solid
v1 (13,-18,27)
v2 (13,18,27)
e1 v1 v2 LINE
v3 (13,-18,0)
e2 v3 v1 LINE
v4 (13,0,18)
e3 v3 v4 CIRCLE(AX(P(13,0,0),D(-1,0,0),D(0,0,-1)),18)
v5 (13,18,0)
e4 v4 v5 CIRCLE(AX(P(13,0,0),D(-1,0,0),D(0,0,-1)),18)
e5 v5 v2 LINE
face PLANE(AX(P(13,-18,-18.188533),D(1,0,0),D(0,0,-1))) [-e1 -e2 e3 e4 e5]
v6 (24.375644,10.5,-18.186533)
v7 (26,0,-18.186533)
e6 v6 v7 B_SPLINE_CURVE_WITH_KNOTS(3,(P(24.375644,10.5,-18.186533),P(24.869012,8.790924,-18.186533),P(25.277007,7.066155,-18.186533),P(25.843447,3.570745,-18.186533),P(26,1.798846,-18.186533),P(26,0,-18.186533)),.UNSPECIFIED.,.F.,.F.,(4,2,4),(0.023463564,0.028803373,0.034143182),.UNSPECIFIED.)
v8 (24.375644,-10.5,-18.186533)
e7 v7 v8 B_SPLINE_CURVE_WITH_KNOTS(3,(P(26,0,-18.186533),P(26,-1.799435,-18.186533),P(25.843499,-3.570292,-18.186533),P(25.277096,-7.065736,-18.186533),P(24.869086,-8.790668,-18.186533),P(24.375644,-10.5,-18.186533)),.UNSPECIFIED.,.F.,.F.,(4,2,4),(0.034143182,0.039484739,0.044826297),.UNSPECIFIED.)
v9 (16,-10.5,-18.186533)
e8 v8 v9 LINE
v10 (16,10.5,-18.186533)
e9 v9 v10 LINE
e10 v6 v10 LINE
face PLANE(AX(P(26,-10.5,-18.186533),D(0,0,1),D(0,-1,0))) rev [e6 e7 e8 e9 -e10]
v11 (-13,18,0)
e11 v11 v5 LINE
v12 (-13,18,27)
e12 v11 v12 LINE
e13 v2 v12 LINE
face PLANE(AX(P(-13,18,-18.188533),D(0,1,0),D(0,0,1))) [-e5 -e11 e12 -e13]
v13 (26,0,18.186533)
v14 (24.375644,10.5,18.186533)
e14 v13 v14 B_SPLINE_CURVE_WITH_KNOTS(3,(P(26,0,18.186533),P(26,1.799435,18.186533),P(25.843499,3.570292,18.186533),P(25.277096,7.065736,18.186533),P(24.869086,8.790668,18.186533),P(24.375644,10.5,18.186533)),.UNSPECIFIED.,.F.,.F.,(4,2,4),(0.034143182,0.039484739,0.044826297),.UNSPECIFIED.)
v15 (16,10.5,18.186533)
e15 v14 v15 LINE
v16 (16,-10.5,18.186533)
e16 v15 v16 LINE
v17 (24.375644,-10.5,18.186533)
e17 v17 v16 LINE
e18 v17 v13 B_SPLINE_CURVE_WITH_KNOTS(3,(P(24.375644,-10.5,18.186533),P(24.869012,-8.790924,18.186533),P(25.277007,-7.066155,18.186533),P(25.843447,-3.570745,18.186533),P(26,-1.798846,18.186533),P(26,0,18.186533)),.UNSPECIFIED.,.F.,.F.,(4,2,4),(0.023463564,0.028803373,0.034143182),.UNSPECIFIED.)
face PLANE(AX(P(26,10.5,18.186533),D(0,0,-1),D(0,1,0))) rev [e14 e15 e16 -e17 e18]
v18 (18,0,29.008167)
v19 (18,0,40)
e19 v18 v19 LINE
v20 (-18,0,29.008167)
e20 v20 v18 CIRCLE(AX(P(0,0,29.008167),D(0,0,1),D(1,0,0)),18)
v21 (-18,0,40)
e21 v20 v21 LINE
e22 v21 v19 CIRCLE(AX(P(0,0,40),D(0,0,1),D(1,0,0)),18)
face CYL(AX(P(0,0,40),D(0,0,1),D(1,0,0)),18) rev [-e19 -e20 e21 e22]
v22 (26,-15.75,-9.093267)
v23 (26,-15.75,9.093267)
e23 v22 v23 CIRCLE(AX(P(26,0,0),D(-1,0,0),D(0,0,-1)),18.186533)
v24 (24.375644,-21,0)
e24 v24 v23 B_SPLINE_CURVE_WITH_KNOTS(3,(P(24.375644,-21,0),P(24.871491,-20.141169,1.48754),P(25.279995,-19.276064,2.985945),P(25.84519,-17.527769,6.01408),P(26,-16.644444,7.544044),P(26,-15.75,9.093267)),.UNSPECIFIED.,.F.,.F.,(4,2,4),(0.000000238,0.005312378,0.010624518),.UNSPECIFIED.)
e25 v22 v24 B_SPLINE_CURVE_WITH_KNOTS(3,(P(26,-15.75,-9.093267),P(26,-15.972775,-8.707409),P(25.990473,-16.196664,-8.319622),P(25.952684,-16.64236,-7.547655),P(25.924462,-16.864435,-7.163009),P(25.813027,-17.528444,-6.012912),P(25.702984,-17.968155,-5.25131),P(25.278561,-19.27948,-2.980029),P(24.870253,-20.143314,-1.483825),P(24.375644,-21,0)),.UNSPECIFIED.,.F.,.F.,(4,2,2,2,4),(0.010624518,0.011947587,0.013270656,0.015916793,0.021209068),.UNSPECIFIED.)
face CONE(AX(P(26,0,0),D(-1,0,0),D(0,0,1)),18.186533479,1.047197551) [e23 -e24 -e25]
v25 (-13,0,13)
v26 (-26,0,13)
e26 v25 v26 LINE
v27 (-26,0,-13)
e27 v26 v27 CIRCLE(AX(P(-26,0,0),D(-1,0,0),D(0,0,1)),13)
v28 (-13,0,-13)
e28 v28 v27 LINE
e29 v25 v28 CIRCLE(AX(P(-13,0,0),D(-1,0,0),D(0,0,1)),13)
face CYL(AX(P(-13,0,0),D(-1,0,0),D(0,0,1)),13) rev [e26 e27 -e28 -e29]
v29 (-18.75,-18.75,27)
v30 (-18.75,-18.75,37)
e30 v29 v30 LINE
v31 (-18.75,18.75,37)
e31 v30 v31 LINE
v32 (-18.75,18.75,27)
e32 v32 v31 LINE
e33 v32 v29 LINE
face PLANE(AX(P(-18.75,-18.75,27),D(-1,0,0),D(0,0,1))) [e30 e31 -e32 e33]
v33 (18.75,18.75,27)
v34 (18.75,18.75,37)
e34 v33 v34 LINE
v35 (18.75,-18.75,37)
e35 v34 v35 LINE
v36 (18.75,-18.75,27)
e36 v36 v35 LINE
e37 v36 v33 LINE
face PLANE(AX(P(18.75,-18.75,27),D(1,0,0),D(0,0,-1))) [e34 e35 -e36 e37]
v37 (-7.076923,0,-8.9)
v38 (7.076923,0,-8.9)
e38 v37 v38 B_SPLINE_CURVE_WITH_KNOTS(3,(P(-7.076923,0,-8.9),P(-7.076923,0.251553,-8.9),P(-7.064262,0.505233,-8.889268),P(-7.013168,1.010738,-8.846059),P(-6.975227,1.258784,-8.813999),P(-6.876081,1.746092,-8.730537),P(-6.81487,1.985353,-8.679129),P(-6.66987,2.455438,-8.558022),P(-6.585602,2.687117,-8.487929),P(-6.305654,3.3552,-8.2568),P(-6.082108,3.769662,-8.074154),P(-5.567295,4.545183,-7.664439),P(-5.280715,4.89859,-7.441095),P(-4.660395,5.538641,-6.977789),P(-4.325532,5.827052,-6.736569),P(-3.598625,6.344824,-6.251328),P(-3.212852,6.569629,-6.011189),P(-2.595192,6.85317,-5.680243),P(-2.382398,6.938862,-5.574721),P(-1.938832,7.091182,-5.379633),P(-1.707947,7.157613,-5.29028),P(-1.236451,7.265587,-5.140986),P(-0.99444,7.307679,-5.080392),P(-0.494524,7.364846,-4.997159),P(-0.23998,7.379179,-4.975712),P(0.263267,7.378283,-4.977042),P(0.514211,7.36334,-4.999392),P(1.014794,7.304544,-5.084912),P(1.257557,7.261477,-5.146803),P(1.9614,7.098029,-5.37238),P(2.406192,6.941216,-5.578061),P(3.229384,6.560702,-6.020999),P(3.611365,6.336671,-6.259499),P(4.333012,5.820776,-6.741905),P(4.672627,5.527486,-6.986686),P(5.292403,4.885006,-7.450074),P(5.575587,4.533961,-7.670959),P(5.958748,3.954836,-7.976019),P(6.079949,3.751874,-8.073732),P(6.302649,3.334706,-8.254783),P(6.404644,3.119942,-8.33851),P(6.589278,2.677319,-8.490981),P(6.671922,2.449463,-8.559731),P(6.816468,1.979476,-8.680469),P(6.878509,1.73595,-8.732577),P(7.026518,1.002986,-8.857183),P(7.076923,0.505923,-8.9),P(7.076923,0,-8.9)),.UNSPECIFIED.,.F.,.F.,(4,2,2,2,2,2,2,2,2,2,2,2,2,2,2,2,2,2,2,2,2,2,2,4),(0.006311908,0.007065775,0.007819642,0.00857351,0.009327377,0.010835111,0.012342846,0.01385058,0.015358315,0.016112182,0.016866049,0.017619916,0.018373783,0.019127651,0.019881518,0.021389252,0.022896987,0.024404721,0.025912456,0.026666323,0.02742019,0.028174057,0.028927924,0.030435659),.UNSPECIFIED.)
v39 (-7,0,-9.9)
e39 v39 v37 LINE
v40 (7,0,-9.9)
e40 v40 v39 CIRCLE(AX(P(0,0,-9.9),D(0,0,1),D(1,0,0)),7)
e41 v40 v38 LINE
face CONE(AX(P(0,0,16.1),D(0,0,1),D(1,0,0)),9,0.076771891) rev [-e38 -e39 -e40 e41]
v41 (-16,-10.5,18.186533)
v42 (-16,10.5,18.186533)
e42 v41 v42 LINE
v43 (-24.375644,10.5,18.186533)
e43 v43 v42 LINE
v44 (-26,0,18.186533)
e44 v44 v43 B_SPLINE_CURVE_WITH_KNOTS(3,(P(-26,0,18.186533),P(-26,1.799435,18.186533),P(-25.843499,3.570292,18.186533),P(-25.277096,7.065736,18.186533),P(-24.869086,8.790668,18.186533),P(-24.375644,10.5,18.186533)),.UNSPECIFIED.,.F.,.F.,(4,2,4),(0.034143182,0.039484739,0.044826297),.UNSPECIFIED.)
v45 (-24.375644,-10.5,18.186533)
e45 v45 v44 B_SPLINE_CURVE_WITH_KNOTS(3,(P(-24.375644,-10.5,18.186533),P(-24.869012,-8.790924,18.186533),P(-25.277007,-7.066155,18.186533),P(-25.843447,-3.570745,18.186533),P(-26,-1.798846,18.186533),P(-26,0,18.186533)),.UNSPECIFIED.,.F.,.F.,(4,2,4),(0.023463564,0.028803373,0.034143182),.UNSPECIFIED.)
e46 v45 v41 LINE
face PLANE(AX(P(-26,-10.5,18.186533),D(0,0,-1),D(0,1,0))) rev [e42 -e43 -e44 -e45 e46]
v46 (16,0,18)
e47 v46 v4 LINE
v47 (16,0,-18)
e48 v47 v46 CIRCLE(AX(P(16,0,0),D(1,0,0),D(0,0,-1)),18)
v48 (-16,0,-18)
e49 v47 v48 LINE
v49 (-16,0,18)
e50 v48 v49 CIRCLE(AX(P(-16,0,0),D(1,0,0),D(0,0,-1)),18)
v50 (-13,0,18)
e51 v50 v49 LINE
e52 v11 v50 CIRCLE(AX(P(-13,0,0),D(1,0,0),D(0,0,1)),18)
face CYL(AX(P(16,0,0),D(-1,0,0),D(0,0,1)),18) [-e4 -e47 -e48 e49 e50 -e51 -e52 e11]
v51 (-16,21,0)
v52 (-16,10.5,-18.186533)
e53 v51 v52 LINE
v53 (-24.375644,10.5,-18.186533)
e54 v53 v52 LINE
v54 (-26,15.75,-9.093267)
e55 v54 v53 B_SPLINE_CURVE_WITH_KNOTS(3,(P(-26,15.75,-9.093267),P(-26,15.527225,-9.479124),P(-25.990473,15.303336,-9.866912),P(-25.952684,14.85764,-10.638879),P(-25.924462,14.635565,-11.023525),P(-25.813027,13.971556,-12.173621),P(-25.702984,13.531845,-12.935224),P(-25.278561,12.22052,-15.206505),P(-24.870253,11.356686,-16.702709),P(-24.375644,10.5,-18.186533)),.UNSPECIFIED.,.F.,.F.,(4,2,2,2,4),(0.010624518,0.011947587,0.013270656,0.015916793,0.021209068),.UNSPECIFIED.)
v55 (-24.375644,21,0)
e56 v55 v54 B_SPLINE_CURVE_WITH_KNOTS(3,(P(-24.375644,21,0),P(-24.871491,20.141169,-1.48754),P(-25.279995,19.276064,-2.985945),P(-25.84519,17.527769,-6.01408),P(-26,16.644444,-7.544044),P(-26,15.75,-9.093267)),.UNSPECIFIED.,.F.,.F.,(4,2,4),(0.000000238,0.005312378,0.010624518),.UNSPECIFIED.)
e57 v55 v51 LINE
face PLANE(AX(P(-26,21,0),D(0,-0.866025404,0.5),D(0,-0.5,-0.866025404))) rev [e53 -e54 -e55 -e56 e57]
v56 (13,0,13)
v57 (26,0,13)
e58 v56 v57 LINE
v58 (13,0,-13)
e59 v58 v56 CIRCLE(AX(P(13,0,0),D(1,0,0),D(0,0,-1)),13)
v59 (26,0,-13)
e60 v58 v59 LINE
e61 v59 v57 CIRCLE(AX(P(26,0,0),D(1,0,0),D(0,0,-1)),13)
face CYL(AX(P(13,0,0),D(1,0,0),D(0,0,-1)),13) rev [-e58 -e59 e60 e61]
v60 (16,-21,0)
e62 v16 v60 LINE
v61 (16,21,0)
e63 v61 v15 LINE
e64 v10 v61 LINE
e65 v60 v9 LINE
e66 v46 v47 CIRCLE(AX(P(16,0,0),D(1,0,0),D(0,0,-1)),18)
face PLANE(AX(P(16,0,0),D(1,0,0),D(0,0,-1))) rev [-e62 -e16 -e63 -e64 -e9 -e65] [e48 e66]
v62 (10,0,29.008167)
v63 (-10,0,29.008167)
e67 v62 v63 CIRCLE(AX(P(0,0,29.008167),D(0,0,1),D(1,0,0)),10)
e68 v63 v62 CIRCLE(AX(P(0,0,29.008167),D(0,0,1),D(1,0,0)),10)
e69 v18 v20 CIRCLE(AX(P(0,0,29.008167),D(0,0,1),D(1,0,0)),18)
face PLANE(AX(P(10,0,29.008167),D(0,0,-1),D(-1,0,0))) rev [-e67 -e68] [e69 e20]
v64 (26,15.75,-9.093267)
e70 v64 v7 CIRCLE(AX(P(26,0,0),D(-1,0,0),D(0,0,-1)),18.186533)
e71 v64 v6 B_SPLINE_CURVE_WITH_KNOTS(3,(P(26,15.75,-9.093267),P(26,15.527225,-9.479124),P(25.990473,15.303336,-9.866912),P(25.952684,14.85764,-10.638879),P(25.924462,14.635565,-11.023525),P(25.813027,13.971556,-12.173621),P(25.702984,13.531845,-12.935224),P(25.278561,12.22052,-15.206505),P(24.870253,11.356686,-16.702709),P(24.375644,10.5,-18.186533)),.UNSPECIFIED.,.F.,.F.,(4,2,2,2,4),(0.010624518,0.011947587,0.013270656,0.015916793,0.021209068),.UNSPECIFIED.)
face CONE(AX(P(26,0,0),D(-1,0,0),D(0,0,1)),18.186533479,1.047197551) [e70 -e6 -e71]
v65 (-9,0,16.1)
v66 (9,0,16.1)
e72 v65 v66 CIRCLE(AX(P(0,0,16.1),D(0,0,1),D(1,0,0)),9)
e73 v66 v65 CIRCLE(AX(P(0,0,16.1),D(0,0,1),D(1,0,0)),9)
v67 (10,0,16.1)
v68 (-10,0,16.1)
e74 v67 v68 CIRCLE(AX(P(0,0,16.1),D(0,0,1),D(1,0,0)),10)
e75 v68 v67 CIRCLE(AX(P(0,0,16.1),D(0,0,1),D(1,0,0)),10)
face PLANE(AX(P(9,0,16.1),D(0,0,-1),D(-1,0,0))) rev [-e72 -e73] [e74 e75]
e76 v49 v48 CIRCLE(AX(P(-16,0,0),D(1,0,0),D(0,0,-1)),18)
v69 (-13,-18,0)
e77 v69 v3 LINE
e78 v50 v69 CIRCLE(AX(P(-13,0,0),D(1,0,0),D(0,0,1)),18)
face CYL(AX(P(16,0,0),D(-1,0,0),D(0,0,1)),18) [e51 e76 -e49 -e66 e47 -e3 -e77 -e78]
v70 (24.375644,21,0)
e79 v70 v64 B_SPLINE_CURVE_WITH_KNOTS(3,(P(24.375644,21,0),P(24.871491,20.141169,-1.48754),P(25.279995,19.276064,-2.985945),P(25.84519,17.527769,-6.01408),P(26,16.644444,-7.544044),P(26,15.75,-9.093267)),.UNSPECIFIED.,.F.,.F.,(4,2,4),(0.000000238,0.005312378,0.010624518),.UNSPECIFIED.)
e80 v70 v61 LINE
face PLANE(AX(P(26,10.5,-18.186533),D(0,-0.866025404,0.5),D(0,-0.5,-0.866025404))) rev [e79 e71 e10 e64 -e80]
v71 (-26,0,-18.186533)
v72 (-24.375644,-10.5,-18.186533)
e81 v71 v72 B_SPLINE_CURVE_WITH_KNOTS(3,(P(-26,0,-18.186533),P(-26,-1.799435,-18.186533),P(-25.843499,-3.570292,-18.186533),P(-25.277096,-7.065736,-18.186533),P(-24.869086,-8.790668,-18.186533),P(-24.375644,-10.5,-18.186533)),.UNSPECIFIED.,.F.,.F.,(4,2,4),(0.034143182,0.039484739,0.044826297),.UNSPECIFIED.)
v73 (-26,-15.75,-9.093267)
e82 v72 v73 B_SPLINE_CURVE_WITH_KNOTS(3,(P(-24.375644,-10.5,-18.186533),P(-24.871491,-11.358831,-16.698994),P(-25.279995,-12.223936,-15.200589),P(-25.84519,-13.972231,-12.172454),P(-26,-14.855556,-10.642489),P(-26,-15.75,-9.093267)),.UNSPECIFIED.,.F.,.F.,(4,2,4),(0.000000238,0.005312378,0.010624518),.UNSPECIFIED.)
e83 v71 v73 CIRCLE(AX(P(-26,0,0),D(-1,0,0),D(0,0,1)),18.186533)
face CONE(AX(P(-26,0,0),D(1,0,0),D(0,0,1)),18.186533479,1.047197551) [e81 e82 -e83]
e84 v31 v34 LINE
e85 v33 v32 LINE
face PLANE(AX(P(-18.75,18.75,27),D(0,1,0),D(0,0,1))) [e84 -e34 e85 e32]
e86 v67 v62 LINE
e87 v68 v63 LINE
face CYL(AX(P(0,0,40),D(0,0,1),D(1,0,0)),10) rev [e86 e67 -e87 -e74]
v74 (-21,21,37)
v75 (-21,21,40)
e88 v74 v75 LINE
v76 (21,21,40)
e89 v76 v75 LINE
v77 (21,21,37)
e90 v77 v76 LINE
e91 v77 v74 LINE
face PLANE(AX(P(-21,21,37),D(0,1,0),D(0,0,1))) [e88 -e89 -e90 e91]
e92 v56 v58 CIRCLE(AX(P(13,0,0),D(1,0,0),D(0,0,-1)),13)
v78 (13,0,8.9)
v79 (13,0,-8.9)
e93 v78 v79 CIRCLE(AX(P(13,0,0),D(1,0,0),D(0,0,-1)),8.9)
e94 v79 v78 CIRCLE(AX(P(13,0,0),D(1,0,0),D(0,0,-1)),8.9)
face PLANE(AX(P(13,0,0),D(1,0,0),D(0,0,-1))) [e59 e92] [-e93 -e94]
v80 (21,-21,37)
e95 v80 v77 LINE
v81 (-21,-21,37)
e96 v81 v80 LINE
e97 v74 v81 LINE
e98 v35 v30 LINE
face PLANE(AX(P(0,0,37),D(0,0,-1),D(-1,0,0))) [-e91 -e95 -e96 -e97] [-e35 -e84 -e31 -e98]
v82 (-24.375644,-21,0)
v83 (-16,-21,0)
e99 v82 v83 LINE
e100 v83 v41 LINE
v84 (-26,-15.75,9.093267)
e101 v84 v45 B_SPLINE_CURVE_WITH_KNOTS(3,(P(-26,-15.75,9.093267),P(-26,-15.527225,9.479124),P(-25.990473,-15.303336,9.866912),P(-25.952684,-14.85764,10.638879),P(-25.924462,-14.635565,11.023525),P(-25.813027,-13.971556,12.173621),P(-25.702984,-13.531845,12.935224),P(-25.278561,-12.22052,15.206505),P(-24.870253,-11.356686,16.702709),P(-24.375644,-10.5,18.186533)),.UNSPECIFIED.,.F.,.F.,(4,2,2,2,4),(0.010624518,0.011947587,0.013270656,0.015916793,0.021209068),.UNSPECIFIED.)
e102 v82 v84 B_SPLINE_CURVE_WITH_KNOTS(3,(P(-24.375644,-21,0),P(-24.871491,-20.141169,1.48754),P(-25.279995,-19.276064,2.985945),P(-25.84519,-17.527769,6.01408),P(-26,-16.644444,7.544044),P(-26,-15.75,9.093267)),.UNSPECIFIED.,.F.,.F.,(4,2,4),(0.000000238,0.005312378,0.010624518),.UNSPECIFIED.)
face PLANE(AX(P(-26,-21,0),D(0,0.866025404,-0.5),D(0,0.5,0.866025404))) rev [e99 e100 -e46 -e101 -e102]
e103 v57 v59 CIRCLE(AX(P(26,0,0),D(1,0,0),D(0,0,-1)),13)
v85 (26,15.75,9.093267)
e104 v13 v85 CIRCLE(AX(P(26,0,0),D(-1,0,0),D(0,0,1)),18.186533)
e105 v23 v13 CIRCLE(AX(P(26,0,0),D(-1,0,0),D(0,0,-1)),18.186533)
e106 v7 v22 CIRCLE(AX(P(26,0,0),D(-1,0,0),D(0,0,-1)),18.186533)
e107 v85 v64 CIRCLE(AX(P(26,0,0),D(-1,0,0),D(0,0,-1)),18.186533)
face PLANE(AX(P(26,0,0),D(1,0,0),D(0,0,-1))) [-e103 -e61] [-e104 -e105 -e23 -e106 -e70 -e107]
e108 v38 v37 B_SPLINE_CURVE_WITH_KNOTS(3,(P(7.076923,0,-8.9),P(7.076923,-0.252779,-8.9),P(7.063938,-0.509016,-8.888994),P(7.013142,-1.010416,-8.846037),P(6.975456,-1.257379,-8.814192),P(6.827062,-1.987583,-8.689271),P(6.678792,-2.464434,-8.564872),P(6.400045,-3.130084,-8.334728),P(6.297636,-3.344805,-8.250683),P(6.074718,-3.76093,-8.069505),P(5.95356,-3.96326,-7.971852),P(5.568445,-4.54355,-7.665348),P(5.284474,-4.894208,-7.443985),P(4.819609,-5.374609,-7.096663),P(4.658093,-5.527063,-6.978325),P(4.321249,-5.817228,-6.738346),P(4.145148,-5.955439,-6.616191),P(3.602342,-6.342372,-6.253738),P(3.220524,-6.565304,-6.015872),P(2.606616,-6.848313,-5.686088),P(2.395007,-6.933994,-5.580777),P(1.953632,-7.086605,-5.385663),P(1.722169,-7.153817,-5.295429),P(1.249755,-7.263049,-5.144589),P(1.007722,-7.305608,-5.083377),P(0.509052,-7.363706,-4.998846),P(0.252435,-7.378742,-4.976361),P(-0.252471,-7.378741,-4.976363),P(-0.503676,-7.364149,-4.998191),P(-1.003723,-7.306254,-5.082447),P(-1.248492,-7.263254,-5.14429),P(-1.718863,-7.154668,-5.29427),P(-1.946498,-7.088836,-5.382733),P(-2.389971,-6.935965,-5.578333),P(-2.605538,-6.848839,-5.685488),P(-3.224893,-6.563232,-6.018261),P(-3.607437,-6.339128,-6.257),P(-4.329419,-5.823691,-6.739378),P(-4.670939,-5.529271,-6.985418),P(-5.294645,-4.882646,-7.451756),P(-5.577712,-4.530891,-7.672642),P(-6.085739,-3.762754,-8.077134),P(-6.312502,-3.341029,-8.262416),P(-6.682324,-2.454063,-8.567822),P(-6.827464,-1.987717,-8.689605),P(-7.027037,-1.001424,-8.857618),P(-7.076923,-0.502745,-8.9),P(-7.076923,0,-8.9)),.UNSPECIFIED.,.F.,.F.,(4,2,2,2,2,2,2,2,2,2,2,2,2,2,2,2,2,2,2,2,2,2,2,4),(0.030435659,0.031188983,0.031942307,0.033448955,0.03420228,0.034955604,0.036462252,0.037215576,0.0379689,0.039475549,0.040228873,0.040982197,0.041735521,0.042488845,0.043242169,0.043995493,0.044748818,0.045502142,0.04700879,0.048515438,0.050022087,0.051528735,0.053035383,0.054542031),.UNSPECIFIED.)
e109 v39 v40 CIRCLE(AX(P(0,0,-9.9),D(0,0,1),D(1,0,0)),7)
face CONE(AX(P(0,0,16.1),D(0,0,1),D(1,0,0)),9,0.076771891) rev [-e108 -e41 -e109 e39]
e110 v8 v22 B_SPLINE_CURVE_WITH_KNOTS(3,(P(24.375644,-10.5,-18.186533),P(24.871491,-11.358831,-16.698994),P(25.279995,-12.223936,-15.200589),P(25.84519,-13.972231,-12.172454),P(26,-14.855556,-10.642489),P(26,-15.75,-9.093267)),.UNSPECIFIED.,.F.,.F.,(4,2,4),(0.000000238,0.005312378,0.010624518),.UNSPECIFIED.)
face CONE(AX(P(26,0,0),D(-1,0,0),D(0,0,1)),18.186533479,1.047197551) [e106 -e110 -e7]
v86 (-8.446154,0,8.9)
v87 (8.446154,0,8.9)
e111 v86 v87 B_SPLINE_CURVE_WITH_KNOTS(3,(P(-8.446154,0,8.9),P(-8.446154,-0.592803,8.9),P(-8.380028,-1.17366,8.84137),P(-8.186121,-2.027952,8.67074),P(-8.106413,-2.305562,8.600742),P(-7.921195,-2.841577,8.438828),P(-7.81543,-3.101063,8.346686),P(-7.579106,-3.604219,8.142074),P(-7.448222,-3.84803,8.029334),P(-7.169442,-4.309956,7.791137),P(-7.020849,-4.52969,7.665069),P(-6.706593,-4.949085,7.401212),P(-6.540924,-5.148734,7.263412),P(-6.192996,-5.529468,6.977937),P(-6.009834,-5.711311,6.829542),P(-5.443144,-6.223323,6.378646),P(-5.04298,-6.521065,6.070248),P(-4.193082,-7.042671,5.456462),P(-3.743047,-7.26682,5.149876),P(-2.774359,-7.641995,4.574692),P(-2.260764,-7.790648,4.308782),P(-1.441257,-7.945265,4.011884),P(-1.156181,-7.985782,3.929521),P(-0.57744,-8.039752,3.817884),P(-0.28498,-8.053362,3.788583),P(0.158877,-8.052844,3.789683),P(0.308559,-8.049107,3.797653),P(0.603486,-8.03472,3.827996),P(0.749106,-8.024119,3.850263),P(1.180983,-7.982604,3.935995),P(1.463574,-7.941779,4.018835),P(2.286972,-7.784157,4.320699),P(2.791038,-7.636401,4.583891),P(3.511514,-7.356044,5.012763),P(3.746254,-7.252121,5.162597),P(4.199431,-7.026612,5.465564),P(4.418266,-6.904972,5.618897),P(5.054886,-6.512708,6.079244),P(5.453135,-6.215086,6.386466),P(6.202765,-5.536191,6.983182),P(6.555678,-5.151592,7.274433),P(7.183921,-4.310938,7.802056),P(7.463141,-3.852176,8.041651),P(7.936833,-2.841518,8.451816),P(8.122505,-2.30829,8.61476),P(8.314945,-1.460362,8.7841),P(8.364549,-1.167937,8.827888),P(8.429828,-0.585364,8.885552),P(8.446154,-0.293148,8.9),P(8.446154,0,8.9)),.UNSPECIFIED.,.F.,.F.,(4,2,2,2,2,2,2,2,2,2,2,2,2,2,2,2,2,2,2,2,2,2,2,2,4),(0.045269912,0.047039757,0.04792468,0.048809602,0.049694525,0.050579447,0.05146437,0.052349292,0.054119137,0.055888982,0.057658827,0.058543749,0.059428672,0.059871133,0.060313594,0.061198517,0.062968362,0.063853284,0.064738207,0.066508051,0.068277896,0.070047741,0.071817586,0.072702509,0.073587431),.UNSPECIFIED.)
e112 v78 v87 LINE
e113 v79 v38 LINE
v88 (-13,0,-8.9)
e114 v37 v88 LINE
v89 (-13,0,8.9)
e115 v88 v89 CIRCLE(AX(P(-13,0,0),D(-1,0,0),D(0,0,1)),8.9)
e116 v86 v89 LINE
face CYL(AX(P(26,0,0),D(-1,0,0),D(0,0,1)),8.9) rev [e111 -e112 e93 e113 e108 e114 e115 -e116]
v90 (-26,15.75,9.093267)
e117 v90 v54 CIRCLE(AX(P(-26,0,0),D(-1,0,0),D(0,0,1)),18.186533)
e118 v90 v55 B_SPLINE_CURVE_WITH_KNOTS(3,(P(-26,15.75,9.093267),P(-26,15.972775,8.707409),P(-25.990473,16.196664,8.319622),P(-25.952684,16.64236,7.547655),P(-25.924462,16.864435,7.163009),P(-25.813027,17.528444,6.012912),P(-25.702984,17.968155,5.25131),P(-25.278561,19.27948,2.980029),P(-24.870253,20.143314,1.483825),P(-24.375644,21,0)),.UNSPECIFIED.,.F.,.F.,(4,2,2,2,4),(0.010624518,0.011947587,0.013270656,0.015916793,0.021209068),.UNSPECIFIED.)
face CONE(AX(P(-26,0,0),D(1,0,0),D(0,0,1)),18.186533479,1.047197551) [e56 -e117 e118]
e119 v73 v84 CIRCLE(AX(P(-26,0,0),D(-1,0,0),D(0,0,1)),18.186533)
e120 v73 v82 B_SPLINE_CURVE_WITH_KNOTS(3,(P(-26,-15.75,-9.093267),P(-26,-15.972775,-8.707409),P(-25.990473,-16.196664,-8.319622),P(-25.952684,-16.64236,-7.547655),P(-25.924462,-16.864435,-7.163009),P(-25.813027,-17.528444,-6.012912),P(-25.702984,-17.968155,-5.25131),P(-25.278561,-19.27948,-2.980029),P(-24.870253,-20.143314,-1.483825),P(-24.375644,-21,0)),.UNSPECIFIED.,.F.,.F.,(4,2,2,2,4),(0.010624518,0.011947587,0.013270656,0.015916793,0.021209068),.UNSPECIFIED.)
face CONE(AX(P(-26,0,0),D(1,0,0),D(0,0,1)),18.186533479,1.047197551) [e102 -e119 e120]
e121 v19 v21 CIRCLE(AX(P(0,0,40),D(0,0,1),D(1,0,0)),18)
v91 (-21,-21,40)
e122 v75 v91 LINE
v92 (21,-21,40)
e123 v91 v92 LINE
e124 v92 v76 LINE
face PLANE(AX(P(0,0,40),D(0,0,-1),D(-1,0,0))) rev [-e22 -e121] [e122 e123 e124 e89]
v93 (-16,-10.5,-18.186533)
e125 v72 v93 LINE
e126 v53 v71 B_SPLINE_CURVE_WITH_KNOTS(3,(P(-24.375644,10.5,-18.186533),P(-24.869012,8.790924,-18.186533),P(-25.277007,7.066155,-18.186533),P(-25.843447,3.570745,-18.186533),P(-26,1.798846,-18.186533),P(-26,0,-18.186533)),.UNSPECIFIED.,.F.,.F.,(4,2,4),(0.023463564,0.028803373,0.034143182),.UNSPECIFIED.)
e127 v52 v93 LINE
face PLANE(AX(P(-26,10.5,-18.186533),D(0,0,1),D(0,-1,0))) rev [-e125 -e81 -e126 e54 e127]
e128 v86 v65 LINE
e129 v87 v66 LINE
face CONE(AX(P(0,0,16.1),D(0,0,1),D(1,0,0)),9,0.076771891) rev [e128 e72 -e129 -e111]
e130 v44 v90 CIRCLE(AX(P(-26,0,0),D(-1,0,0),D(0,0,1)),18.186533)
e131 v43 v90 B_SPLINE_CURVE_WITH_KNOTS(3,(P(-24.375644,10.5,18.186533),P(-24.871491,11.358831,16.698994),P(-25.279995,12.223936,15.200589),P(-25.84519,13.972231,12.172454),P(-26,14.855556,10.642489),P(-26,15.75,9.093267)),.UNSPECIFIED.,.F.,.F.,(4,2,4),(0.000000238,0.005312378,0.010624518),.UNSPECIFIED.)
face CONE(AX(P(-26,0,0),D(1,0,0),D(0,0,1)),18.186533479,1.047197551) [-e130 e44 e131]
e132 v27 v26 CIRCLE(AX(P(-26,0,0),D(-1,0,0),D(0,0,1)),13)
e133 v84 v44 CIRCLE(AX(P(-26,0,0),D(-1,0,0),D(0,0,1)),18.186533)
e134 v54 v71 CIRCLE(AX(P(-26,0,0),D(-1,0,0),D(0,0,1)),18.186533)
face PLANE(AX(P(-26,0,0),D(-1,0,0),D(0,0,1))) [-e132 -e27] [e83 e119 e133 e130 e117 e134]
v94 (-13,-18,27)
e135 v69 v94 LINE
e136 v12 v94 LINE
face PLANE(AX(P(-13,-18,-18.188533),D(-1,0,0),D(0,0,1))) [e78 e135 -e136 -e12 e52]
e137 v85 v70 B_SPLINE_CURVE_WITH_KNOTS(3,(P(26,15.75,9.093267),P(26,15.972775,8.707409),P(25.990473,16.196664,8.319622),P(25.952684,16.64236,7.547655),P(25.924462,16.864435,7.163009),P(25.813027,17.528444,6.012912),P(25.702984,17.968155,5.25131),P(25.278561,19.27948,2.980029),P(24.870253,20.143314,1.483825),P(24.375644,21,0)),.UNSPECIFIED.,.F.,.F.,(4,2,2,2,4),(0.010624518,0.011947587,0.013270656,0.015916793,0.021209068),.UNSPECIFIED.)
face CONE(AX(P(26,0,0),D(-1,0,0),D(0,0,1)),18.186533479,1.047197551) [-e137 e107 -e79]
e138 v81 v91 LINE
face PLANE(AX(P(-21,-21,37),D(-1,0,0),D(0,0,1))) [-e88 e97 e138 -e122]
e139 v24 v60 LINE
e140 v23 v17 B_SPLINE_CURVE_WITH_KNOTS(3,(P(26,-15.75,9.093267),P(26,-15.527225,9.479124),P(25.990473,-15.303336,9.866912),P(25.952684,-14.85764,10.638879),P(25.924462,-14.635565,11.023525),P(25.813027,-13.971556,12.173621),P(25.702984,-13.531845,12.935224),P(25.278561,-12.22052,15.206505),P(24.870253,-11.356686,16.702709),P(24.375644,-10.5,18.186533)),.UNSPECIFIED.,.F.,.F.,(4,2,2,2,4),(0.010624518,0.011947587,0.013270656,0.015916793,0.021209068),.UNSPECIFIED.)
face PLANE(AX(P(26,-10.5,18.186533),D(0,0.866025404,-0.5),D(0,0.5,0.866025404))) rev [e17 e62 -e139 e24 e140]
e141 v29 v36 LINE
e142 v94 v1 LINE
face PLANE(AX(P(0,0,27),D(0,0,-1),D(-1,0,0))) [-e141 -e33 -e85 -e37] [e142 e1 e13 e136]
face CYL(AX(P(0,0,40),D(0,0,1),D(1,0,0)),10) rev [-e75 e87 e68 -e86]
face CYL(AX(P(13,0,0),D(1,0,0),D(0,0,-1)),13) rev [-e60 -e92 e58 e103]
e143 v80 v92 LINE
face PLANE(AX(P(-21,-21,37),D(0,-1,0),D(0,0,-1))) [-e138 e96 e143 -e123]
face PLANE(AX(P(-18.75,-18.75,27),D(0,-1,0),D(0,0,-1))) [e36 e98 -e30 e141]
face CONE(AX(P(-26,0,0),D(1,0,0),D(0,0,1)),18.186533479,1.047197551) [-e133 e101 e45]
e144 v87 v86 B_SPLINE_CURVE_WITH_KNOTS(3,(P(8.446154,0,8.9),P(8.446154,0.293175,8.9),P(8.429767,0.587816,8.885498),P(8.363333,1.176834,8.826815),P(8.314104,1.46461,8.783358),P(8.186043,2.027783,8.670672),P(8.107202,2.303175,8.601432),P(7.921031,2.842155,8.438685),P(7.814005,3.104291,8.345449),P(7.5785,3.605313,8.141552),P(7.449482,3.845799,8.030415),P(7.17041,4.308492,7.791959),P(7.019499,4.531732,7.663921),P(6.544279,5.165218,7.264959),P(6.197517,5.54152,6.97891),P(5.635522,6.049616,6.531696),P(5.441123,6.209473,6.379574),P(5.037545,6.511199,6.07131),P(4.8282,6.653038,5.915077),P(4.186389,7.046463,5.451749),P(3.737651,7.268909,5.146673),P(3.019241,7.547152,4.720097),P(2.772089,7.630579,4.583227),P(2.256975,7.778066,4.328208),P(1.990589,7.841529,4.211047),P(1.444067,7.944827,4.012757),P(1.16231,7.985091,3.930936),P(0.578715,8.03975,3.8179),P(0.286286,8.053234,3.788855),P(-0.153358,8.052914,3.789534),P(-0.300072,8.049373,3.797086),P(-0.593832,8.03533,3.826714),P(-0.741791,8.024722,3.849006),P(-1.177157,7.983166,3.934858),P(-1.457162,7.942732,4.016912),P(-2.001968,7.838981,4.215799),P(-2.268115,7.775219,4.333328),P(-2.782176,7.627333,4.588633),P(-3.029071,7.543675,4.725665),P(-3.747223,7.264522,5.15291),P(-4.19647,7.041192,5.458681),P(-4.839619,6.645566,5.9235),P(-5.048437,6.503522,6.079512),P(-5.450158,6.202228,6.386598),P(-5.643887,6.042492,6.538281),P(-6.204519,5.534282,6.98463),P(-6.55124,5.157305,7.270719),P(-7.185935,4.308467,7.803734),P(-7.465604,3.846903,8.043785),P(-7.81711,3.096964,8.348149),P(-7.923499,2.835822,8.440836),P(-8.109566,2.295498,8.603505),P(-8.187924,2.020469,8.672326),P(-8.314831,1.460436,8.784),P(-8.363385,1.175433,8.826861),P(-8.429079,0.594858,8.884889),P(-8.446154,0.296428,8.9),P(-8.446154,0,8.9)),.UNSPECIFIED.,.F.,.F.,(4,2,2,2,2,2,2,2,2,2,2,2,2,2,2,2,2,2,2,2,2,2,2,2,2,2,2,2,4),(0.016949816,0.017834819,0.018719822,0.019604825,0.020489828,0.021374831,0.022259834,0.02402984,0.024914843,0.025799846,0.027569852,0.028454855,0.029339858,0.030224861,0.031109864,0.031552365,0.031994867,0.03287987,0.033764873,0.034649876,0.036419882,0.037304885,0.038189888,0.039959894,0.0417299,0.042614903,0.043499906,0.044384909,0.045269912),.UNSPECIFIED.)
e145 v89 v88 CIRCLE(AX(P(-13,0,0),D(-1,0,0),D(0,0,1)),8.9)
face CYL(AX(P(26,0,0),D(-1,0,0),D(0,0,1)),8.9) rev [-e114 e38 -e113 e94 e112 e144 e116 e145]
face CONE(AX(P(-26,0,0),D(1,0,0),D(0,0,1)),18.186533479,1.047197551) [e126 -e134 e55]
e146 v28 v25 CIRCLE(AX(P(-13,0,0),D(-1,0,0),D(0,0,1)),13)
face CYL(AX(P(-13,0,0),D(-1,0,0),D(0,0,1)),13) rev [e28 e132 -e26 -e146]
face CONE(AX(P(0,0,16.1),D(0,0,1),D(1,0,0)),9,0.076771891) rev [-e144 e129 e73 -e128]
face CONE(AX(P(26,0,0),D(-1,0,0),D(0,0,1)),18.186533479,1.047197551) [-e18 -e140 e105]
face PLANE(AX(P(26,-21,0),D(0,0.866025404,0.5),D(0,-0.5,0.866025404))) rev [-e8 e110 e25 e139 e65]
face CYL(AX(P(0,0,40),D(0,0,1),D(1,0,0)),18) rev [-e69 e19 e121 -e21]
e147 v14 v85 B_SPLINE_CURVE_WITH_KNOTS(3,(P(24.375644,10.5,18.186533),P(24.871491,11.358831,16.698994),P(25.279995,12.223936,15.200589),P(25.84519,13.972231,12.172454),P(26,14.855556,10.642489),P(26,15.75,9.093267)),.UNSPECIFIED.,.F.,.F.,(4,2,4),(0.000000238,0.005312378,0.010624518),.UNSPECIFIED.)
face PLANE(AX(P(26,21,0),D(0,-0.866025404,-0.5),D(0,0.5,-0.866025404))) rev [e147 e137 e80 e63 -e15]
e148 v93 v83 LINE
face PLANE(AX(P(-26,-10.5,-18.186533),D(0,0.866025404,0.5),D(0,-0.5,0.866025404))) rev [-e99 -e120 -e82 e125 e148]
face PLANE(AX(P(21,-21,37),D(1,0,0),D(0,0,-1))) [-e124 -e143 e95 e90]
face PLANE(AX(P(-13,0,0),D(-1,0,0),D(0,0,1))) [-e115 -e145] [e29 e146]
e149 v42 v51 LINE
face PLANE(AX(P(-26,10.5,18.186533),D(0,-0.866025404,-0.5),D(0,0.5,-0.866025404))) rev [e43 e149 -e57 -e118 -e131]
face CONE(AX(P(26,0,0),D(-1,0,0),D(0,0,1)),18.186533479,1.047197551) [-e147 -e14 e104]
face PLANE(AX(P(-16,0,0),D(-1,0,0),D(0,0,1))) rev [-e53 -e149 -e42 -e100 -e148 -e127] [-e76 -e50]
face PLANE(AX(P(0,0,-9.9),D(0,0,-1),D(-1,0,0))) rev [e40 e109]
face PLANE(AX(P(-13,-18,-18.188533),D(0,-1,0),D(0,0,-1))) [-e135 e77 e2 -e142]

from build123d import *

# Parameters (mm, degrees)
BODY_PROFILE_36_R                  = 18
BODY_CYLINDER_36_DEPTH             = 16
HEX_END_A_DEPTH                    = 10
HEX_END_B_DEPTH                    = 10
COUNTERBORE_PROFILE_END_A_26_R     = 13
COUNTERBORE_END_A_26_DEPTH         = 13
COUNTERBORE_START                  = -13
COUNTERBORE_PROFILE_END_B_26_R     = 13
COUNTERBORE_END_B_26_DEPTH         = 13
THROUGH_BORE_PROFILE_17_8_R        = 8.9
THROUGH_BORE_17_8_DEPTH            = 48.882669099
HEX_CHAMFER_PROFILE_OUTSIDE_W      = 70.914
HEX_CHAMFER_PROFILE_OUTSIDE_H      = 76.54
HEX_CHAMFER_PROFILE_OUTSIDE_R      = 18.186533479
HEX_CHAMFER_60_DEPTH               = 5
HEX_CHAMFER_60_DRAFT               = -60
HEX_CHAMFER_MIRROR_COPY_1_SKETCH_W = 70.914
HEX_CHAMFER_MIRROR_COPY_1_SKETCH_H = 76.54
HEX_CHAMFER_MIRROR_COPY_1_SKETCH_R = 18.186533479
HEX_CHAMFER_MIRROR_COPY_1_DEPTH    = 5
HEX_CHAMFER_MIRROR_COPY_1_DRAFT    = -60
FLANGE_PROFILE_42X42_W             = 42
FLANGE_PROFILE_42X42_H             = 42
SQUARE_FLANGE_42X42_DEPTH          = 3
SQUARE_BOSS_PROFILE_37_5X37_5_W    = 37.5
SQUARE_BOSS_PROFILE_37_5X37_5_H    = 37.5
SQUARE_BOSS_37_5X37_5_DEPTH        = 13
NECK_BLOCK_36X26_REACH             = 69.102
NECK_BLOCK_36X26_END_RADIUS        = 18
NECK_BLOCK_PROFILE_36X26_W         = 26
NECK_BLOCK_PROFILE_36X26_H         = 36


with BuildPart() as part:
    # Body Profile Ø36 → Body Cylinder Ø36 (new, symmetric)
    with BuildSketch(Plane(origin=(0, 0, 0), x_dir=(0, 0, -1), z_dir=(1, 0, 0))):
        Circle(BODY_PROFILE_36_R)
    extrude(amount=BODY_CYLINDER_36_DEPTH, both=True)

    # Hex Profile End A 42 → Hex End A (add)
    with BuildSketch(Plane(origin=(16, 0, 0), x_dir=(0, 0, -1), z_dir=(1, 0, 0))):
        Polygon((0, 21), (-18.186533479, 10.5), (-18.186533479, -10.5), (0, -21), (18.186533479, -10.5), (18.186533479, 10.5), align=None)
    extrude(amount=HEX_END_A_DEPTH)

    # Hex Profile End B → Hex End B (add)
    with BuildSketch(Plane.ZY.offset(16)):
        Polygon((18.186533479, 10.5), (0, 21), (-18.186533479, 10.5), (-18.186533479, -10.5), (0, -21), (18.186533479, -10.5), align=None)
    extrude(amount=HEX_END_B_DEPTH)

    # Counterbore Profile End A Ø26 → Counterbore End A Ø26 (cut)
    with BuildSketch(Plane(origin=(26, 0, 0), x_dir=(0, 0, -1), z_dir=(1, 0, 0))):
        Circle(COUNTERBORE_PROFILE_END_A_26_R)
    extrude(amount=-COUNTERBORE_END_A_26_DEPTH, mode=Mode.SUBTRACT)

    # Counterbore Profile End B Ø26 → Counterbore End B Ø26 (cut)
    with BuildSketch(Plane.ZY.offset(26).offset(COUNTERBORE_START)):
        with Locations(Location((0, 0, 0), (0, 0, 180))):
            Circle(COUNTERBORE_PROFILE_END_B_26_R)
    extrude(amount=COUNTERBORE_END_B_26_DEPTH, mode=Mode.SUBTRACT)

    # Through Bore Profile Ø17.8 → Through Bore Ø17.8 (cut, through all)
    with BuildSketch(Plane.ZY.offset(13)):
        Circle(THROUGH_BORE_PROFILE_17_8_R)
    extrude(amount=-THROUGH_BORE_17_8_DEPTH, mode=Mode.SUBTRACT)


with BuildPart() as hex_chamfer_60_tool:
    # Hex Chamfer Profile outside → Hex Chamfer 60° (with draft: the straight prism first)
    with BuildSketch(Plane.ZY.offset(26)):
        Rectangle(HEX_CHAMFER_PROFILE_OUTSIDE_W, HEX_CHAMFER_PROFILE_OUTSIDE_H)
        Circle(HEX_CHAMFER_PROFILE_OUTSIDE_R, mode=Mode.SUBTRACT)
    extrude(amount=-HEX_CHAMFER_60_DEPTH)
    # Hex Chamfer 60°: the draft: its side faces are tilted about the plane it starts from
    hex_chamfer_60_sides = [hex_chamfer_60_tool.faces().sort_by_distance(p)[0] for p in [
        (-23.5, -38.27, 0),
        (-23.5, 0, 35.457),
        (-23.5, 38.27, 0),
        (-23.5, 0, -35.457),
        (-23.5, 0, -18.186533479),
    ]]
    draft(hex_chamfer_60_sides, Plane.ZY.offset(26), HEX_CHAMFER_60_DRAFT)


with BuildPart() as part_1:
    add(part.part)

    # Hex Chamfer 60°: cut by hex_chamfer_60_tool
    add(hex_chamfer_60_tool.part, mode=Mode.SUBTRACT)


with BuildPart() as hex_chamfer_mirror_copy_1_tool:
    # Hex Chamfer Mirror copy 1 sketch → Hex Chamfer Mirror copy 1 (with draft: the straight prism first)
    with BuildSketch(Plane(origin=(26, 0, 0), x_dir=(0, 0, 1), z_dir=(1, 0, 0))):
        Rectangle(HEX_CHAMFER_MIRROR_COPY_1_SKETCH_W, HEX_CHAMFER_MIRROR_COPY_1_SKETCH_H)
        Circle(HEX_CHAMFER_MIRROR_COPY_1_SKETCH_R, mode=Mode.SUBTRACT)
    extrude(amount=-HEX_CHAMFER_MIRROR_COPY_1_DEPTH)
    # Hex Chamfer Mirror copy 1: the draft: its side faces are tilted about the plane it starts from
    hex_chamfer_mirror_copy_1_sides = [hex_chamfer_mirror_copy_1_tool.faces().sort_by_distance(p)[0] for p in [
        (23.5, -38.27, 0),
        (23.5, 0, 35.457),
        (23.5, 38.27, 0),
        (23.5, 0, -35.457),
        (23.5, 0, -18.186533479),
    ]]
    draft(hex_chamfer_mirror_copy_1_sides, Plane(origin=(26, 0, 0), x_dir=(0, 0, 1), z_dir=(1, 0, 0)), HEX_CHAMFER_MIRROR_COPY_1_DRAFT)


with BuildPart() as part_2:
    add(part_1.part)

    # Hex Chamfer Mirror copy 1: cut by hex_chamfer_mirror_copy_1_tool
    add(hex_chamfer_mirror_copy_1_tool.part, mode=Mode.SUBTRACT)



with BuildPart() as body_2:
    # Flange Profile 42x42 → Square Flange 42x42 (new body)
    with BuildSketch(Plane.XY.offset(40)):
        Rectangle(FLANGE_PROFILE_42X42_W, FLANGE_PROFILE_42X42_H)
    extrude(amount=-SQUARE_FLANGE_42X42_DEPTH)

    # Square Boss Profile 37.5x37.5 → Square Boss 37.5x37.5 (add)
    with BuildSketch(Plane.XY.offset(40)):
        Rectangle(SQUARE_BOSS_PROFILE_37_5X37_5_W, SQUARE_BOSS_PROFILE_37_5X37_5_H)
    extrude(amount=-SQUARE_BOSS_37_5X37_5_DEPTH)


with BuildPart() as part_3:
    add(part_2.part)

    add(body_2.part)  # Neck Block 36x26 merges body 2
    # Neck Block 36x26: up to this cylinder (the profile starts outside it)
    neck_block_36x26_end = Plane(origin=(0, 0, 0), z_dir=(-1, 0, 0)) * Cylinder(NECK_BLOCK_36X26_END_RADIUS, 175.204, mode=Mode.PRIVATE)
    # Neck Block Profile 36x26 → Neck Block 36x26 (add, up to the surface)
    with BuildSketch(Plane.XY.offset(40), mode=Mode.PRIVATE) as neck_block_36x26_sk1:
        Rectangle(NECK_BLOCK_PROFILE_36X26_W, NECK_BLOCK_PROFILE_36X26_H)
    neck_block_36x26_tool1 = extrude(neck_block_36x26_sk1.sketch, amount=-NECK_BLOCK_36X26_REACH, mode=Mode.PRIVATE) - neck_block_36x26_end
    add(neck_block_36x26_tool1.solids().sort_by_distance((0, 0, 40))[0])

    # Port Bore Profile → Port Bore Revolve (revolve, cut)
    with BuildSketch(Plane(origin=(0, 0, 0), x_dir=(1, 0, 0), z_dir=(0, 1, 0))):
        Polygon((0, -40), (0, 9.9), (7, 9.9), (9, -16.1), (10, -16.1), (10, -29.008166862), (18, -29.008166862), (18, -40), align=None)
    revolve(axis=Axis((0, 0, 40), (0, 0, -1)), mode=Mode.SUBTRACT)


solid = part_3.part
